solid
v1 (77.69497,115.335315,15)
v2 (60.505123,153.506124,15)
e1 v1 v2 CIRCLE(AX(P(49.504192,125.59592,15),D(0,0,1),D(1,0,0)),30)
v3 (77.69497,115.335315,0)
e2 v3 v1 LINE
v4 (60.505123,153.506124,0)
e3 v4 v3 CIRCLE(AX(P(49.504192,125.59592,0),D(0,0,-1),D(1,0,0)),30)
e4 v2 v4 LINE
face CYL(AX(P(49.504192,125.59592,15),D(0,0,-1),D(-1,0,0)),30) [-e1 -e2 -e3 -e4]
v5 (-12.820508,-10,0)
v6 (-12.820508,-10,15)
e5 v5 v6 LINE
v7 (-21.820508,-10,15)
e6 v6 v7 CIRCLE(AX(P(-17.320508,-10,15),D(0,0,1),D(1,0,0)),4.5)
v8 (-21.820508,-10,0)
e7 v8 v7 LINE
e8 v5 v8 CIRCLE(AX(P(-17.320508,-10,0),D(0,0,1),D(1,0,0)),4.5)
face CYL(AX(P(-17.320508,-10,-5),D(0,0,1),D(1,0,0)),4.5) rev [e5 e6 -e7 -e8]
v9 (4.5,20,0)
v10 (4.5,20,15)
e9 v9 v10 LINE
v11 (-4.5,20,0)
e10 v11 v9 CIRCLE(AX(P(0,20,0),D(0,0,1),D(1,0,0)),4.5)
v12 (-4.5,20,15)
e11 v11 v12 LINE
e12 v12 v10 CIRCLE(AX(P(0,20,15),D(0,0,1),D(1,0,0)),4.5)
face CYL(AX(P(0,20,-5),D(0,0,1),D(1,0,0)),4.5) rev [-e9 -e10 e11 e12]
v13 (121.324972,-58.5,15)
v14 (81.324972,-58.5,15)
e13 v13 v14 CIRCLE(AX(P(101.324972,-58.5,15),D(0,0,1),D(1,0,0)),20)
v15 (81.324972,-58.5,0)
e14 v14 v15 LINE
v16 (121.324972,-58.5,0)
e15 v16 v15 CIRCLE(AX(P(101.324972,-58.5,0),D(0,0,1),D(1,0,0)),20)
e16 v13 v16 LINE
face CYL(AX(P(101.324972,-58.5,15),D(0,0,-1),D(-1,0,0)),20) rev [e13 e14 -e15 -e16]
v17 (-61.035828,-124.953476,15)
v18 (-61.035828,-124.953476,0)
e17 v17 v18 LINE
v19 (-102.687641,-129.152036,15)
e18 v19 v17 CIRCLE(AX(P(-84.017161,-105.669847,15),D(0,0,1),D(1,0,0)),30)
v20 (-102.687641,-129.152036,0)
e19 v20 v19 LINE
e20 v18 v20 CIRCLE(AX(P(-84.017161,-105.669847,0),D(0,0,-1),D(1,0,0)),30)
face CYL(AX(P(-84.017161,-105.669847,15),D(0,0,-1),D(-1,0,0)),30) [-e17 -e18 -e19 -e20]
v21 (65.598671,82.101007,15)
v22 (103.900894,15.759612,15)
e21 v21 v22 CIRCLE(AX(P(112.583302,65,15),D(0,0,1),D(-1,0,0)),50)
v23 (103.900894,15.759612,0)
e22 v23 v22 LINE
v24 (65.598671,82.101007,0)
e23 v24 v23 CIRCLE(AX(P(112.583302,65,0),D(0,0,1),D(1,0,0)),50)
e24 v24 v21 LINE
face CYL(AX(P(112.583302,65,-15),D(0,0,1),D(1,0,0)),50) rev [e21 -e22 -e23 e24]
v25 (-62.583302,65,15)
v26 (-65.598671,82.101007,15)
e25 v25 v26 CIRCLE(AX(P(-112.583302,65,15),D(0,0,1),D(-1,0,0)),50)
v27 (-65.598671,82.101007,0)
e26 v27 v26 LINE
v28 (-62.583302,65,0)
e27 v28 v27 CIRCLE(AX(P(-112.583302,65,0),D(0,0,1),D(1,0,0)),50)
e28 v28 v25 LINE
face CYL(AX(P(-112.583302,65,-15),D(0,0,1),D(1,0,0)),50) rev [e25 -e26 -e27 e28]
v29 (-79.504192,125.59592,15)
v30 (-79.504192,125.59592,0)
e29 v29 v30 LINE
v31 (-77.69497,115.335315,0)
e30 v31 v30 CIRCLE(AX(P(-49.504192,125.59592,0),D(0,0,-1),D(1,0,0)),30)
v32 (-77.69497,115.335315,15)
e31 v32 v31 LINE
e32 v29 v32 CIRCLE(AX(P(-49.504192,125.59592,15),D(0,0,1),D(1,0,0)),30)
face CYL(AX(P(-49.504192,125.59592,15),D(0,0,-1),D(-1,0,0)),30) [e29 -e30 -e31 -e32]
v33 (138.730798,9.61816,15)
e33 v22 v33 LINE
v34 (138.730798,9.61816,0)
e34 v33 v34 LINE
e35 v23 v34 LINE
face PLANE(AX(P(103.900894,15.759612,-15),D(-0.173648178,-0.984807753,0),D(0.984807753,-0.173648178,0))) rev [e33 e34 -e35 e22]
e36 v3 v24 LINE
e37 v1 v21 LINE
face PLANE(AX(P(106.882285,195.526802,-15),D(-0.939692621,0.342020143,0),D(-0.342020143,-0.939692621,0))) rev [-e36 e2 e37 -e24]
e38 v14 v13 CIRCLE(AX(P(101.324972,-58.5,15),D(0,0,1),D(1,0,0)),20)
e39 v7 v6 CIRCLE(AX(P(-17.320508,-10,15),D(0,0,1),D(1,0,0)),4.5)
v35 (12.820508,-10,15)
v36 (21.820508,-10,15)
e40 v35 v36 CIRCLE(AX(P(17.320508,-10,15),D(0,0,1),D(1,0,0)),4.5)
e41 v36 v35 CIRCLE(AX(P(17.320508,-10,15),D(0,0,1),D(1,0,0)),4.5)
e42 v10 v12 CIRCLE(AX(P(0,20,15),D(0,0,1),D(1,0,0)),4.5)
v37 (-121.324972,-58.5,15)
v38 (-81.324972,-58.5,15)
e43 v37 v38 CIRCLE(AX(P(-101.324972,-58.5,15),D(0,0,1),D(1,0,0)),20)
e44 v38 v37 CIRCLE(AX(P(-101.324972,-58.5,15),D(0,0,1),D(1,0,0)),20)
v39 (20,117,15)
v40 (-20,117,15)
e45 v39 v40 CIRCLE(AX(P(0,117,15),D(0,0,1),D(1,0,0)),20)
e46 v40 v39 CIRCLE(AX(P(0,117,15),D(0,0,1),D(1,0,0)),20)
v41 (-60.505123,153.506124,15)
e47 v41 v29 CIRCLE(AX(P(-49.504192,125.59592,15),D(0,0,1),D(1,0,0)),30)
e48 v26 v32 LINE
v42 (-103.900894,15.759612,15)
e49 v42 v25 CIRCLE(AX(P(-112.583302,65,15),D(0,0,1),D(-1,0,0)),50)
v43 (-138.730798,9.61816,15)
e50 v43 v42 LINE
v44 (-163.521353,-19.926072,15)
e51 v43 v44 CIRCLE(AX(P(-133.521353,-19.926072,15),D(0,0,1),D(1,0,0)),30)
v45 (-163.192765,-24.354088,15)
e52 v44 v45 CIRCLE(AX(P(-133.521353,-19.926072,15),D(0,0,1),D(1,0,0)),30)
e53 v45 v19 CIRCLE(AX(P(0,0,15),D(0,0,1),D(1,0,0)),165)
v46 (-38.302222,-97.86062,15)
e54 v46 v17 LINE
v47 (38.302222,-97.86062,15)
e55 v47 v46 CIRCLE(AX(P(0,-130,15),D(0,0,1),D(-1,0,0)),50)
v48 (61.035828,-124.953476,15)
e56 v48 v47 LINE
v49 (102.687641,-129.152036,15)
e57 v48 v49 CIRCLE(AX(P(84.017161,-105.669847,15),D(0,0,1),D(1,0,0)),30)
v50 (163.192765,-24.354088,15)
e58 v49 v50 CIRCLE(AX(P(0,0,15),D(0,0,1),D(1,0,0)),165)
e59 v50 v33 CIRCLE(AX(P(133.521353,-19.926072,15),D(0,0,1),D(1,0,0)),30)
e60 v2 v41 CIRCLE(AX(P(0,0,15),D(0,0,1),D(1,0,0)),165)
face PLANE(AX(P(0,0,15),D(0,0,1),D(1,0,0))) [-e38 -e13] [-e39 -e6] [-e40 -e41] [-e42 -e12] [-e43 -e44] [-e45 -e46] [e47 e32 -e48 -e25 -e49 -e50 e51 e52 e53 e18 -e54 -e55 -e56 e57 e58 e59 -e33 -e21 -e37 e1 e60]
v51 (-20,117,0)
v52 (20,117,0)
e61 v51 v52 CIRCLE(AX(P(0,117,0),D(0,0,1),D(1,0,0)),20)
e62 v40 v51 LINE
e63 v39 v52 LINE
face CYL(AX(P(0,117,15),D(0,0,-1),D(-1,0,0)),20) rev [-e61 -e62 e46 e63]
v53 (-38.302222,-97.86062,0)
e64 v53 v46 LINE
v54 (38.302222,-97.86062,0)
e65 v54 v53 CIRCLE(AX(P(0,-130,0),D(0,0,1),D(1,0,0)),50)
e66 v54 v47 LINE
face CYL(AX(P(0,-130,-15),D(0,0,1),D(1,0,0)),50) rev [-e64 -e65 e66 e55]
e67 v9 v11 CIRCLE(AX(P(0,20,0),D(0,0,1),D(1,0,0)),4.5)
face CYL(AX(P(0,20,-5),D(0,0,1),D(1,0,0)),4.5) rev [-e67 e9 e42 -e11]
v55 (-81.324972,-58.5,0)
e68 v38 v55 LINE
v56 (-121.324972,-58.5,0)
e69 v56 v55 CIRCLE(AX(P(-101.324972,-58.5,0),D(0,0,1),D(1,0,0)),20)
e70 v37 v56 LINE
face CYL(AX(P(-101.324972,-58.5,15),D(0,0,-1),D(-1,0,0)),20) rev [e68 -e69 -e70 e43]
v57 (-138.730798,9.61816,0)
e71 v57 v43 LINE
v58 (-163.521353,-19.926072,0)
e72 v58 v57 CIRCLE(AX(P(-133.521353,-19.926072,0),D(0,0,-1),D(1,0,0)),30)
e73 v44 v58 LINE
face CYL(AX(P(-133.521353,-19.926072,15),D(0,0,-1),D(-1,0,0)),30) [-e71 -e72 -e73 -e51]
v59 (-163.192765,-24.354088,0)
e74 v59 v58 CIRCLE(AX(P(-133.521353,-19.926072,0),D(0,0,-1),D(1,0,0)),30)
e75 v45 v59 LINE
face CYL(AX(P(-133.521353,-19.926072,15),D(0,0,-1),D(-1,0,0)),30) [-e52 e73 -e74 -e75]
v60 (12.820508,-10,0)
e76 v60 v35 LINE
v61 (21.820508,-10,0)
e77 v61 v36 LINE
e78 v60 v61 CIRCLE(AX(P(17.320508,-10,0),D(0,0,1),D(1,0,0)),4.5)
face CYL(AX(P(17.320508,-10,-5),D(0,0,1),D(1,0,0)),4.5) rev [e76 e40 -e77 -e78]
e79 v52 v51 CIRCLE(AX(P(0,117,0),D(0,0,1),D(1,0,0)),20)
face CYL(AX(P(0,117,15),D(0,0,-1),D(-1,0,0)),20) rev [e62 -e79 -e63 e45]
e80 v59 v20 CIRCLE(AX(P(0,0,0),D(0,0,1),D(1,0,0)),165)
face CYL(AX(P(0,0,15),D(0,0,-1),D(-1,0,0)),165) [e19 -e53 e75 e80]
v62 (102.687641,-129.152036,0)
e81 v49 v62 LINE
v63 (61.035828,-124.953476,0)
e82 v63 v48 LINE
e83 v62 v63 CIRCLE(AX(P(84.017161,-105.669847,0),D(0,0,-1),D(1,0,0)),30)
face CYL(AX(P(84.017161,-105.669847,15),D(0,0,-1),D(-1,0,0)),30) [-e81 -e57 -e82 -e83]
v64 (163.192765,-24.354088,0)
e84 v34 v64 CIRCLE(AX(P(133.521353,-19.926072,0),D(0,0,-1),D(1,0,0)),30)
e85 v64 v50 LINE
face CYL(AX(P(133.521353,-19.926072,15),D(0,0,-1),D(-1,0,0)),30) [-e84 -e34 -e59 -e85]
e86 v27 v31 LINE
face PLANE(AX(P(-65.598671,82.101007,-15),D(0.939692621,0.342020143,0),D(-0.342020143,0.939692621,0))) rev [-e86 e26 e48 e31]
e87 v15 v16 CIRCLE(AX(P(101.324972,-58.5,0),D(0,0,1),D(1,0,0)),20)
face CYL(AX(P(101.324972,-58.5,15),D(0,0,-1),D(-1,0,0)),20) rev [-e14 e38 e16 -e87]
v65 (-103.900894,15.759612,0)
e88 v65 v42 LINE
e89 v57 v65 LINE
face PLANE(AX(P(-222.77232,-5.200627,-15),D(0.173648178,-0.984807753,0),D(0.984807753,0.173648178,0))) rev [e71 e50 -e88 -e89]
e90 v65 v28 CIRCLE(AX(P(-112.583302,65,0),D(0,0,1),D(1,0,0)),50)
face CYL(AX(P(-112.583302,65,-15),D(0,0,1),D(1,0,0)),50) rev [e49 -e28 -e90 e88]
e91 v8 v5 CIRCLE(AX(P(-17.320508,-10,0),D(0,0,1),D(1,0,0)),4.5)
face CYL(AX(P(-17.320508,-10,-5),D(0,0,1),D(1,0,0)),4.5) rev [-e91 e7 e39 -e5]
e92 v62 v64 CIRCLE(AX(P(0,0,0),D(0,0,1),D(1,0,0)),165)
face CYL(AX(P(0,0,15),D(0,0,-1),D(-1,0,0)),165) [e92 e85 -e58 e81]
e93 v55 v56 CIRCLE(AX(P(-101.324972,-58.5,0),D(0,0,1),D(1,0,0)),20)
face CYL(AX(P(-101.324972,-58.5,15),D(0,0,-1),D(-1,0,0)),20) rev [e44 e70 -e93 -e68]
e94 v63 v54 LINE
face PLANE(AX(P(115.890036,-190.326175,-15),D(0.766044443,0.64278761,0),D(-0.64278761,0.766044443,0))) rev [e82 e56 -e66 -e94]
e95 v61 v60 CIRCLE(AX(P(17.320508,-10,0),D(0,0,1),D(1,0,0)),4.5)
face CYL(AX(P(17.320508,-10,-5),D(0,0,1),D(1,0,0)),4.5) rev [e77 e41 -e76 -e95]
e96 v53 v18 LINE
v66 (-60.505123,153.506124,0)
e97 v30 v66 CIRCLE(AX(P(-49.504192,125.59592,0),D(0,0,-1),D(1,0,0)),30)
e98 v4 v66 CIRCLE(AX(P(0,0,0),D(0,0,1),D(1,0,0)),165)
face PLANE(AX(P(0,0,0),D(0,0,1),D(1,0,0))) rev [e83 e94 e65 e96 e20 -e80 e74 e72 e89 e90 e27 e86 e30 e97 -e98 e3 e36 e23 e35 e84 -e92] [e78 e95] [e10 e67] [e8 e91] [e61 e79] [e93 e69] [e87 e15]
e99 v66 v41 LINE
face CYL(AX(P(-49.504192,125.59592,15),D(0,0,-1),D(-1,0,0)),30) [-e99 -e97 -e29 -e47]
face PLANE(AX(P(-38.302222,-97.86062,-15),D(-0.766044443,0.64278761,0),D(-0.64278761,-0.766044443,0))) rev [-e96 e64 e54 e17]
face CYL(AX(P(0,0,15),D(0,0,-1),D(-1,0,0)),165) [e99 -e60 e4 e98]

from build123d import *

# Parameters (mm, degrees)
SKETCH1_R           = 165
SKETCH1_R_2         = 20
BOSS_EXTRUDE1_DEPTH = 15
CUT_EXTRUDE1_DEPTH  = 30
FILLET1_R           = 30
SKETCH3_R           = 4.5
CUT_EXTRUDE2_DEPTH  = 20


with BuildPart() as part:
    # Sketch1 → Boss-Extrude1 (new body)
    with BuildSketch(Plane.XY):
        Circle(SKETCH1_R)
        with Locations((0, 117)):
            Circle(SKETCH1_R_2, mode=Mode.SUBTRACT)
        with Locations((101.324972243, -58.5)):
            Circle(SKETCH1_R_2, mode=Mode.SUBTRACT)
        with Locations((-101.324972243, -58.5)):
            Circle(SKETCH1_R_2, mode=Mode.SUBTRACT)
    extrude(amount=BOSS_EXTRUDE1_DEPTH)

    # Sketch2 → Cut-Extrude1 (cut)
    with BuildSketch(Plane.XY.offset(15)):
        with BuildLine():
            Line((-38.302222156, -97.860619516), (-169.990854036, -254.801019663))
            Line((-169.990854036, -254.801019663), (115.890035572, -190.326174896))
            Line((115.890035572, -190.326174896), (38.302222156, -97.860619516))
            ThreePointArc((38.302222156, -97.860619516), (0, -80), (-38.302222156, -97.860619516))
        make_face()
        with BuildLine():
            Line((-65.598671453, 82.101007166), (-135.66872892, 274.616907838))
            Line((-135.66872892, 274.616907838), (-222.772320251, -5.200627403))
            Line((-222.772320251, -5.200627403), (-103.900893609, 15.759612349))
            ThreePointArc((-103.900893609, 15.759612349), (-69.282032303, 40), (-65.598671453, 82.101007166))
        make_face()
        with BuildLine():
            Line((103.900893609, 15.759612349), (305.659582957, -19.815888175))
            Line((305.659582957, -19.815888175), (106.882284679, 195.526802298))
            Line((106.882284679, 195.526802298), (65.598671453, 82.101007166))
            ThreePointArc((65.598671453, 82.101007166), (69.282032303, 40), (103.900893609, 15.759612349))
        make_face()
    extrude(amount=-CUT_EXTRUDE1_DEPTH, mode=Mode.SUBTRACT)

    # Fillet1
    fillet1_edges = [part.edges().sort_by_distance(p)[0] for p in [
        (164.924238662, 4.999550163, 7.5),
        (86.79185678, 140.328805299, 7.5),
        (-86.79185678, 140.328805299, 7.5),
        (-164.924238662, 4.999550163, 7.5),
        (-78.132381882, -145.328355463, 7.5),
        (78.132381882, -145.328355463, 7.5),
    ]]
    fillet(fillet1_edges, radius=FILLET1_R)

    # Sketch3 → Cut-Extrude2 (cut)
    with BuildSketch(Plane.XY.offset(15)):
        with Locations((0, 20)):
            Circle(SKETCH3_R)
        with Locations((17.320508076, -10)):
            Circle(SKETCH3_R)
        with Locations((-17.320508076, -10)):
            Circle(SKETCH3_R)
    extrude(amount=-CUT_EXTRUDE2_DEPTH, mode=Mode.SUBTRACT)


solid = part.part
